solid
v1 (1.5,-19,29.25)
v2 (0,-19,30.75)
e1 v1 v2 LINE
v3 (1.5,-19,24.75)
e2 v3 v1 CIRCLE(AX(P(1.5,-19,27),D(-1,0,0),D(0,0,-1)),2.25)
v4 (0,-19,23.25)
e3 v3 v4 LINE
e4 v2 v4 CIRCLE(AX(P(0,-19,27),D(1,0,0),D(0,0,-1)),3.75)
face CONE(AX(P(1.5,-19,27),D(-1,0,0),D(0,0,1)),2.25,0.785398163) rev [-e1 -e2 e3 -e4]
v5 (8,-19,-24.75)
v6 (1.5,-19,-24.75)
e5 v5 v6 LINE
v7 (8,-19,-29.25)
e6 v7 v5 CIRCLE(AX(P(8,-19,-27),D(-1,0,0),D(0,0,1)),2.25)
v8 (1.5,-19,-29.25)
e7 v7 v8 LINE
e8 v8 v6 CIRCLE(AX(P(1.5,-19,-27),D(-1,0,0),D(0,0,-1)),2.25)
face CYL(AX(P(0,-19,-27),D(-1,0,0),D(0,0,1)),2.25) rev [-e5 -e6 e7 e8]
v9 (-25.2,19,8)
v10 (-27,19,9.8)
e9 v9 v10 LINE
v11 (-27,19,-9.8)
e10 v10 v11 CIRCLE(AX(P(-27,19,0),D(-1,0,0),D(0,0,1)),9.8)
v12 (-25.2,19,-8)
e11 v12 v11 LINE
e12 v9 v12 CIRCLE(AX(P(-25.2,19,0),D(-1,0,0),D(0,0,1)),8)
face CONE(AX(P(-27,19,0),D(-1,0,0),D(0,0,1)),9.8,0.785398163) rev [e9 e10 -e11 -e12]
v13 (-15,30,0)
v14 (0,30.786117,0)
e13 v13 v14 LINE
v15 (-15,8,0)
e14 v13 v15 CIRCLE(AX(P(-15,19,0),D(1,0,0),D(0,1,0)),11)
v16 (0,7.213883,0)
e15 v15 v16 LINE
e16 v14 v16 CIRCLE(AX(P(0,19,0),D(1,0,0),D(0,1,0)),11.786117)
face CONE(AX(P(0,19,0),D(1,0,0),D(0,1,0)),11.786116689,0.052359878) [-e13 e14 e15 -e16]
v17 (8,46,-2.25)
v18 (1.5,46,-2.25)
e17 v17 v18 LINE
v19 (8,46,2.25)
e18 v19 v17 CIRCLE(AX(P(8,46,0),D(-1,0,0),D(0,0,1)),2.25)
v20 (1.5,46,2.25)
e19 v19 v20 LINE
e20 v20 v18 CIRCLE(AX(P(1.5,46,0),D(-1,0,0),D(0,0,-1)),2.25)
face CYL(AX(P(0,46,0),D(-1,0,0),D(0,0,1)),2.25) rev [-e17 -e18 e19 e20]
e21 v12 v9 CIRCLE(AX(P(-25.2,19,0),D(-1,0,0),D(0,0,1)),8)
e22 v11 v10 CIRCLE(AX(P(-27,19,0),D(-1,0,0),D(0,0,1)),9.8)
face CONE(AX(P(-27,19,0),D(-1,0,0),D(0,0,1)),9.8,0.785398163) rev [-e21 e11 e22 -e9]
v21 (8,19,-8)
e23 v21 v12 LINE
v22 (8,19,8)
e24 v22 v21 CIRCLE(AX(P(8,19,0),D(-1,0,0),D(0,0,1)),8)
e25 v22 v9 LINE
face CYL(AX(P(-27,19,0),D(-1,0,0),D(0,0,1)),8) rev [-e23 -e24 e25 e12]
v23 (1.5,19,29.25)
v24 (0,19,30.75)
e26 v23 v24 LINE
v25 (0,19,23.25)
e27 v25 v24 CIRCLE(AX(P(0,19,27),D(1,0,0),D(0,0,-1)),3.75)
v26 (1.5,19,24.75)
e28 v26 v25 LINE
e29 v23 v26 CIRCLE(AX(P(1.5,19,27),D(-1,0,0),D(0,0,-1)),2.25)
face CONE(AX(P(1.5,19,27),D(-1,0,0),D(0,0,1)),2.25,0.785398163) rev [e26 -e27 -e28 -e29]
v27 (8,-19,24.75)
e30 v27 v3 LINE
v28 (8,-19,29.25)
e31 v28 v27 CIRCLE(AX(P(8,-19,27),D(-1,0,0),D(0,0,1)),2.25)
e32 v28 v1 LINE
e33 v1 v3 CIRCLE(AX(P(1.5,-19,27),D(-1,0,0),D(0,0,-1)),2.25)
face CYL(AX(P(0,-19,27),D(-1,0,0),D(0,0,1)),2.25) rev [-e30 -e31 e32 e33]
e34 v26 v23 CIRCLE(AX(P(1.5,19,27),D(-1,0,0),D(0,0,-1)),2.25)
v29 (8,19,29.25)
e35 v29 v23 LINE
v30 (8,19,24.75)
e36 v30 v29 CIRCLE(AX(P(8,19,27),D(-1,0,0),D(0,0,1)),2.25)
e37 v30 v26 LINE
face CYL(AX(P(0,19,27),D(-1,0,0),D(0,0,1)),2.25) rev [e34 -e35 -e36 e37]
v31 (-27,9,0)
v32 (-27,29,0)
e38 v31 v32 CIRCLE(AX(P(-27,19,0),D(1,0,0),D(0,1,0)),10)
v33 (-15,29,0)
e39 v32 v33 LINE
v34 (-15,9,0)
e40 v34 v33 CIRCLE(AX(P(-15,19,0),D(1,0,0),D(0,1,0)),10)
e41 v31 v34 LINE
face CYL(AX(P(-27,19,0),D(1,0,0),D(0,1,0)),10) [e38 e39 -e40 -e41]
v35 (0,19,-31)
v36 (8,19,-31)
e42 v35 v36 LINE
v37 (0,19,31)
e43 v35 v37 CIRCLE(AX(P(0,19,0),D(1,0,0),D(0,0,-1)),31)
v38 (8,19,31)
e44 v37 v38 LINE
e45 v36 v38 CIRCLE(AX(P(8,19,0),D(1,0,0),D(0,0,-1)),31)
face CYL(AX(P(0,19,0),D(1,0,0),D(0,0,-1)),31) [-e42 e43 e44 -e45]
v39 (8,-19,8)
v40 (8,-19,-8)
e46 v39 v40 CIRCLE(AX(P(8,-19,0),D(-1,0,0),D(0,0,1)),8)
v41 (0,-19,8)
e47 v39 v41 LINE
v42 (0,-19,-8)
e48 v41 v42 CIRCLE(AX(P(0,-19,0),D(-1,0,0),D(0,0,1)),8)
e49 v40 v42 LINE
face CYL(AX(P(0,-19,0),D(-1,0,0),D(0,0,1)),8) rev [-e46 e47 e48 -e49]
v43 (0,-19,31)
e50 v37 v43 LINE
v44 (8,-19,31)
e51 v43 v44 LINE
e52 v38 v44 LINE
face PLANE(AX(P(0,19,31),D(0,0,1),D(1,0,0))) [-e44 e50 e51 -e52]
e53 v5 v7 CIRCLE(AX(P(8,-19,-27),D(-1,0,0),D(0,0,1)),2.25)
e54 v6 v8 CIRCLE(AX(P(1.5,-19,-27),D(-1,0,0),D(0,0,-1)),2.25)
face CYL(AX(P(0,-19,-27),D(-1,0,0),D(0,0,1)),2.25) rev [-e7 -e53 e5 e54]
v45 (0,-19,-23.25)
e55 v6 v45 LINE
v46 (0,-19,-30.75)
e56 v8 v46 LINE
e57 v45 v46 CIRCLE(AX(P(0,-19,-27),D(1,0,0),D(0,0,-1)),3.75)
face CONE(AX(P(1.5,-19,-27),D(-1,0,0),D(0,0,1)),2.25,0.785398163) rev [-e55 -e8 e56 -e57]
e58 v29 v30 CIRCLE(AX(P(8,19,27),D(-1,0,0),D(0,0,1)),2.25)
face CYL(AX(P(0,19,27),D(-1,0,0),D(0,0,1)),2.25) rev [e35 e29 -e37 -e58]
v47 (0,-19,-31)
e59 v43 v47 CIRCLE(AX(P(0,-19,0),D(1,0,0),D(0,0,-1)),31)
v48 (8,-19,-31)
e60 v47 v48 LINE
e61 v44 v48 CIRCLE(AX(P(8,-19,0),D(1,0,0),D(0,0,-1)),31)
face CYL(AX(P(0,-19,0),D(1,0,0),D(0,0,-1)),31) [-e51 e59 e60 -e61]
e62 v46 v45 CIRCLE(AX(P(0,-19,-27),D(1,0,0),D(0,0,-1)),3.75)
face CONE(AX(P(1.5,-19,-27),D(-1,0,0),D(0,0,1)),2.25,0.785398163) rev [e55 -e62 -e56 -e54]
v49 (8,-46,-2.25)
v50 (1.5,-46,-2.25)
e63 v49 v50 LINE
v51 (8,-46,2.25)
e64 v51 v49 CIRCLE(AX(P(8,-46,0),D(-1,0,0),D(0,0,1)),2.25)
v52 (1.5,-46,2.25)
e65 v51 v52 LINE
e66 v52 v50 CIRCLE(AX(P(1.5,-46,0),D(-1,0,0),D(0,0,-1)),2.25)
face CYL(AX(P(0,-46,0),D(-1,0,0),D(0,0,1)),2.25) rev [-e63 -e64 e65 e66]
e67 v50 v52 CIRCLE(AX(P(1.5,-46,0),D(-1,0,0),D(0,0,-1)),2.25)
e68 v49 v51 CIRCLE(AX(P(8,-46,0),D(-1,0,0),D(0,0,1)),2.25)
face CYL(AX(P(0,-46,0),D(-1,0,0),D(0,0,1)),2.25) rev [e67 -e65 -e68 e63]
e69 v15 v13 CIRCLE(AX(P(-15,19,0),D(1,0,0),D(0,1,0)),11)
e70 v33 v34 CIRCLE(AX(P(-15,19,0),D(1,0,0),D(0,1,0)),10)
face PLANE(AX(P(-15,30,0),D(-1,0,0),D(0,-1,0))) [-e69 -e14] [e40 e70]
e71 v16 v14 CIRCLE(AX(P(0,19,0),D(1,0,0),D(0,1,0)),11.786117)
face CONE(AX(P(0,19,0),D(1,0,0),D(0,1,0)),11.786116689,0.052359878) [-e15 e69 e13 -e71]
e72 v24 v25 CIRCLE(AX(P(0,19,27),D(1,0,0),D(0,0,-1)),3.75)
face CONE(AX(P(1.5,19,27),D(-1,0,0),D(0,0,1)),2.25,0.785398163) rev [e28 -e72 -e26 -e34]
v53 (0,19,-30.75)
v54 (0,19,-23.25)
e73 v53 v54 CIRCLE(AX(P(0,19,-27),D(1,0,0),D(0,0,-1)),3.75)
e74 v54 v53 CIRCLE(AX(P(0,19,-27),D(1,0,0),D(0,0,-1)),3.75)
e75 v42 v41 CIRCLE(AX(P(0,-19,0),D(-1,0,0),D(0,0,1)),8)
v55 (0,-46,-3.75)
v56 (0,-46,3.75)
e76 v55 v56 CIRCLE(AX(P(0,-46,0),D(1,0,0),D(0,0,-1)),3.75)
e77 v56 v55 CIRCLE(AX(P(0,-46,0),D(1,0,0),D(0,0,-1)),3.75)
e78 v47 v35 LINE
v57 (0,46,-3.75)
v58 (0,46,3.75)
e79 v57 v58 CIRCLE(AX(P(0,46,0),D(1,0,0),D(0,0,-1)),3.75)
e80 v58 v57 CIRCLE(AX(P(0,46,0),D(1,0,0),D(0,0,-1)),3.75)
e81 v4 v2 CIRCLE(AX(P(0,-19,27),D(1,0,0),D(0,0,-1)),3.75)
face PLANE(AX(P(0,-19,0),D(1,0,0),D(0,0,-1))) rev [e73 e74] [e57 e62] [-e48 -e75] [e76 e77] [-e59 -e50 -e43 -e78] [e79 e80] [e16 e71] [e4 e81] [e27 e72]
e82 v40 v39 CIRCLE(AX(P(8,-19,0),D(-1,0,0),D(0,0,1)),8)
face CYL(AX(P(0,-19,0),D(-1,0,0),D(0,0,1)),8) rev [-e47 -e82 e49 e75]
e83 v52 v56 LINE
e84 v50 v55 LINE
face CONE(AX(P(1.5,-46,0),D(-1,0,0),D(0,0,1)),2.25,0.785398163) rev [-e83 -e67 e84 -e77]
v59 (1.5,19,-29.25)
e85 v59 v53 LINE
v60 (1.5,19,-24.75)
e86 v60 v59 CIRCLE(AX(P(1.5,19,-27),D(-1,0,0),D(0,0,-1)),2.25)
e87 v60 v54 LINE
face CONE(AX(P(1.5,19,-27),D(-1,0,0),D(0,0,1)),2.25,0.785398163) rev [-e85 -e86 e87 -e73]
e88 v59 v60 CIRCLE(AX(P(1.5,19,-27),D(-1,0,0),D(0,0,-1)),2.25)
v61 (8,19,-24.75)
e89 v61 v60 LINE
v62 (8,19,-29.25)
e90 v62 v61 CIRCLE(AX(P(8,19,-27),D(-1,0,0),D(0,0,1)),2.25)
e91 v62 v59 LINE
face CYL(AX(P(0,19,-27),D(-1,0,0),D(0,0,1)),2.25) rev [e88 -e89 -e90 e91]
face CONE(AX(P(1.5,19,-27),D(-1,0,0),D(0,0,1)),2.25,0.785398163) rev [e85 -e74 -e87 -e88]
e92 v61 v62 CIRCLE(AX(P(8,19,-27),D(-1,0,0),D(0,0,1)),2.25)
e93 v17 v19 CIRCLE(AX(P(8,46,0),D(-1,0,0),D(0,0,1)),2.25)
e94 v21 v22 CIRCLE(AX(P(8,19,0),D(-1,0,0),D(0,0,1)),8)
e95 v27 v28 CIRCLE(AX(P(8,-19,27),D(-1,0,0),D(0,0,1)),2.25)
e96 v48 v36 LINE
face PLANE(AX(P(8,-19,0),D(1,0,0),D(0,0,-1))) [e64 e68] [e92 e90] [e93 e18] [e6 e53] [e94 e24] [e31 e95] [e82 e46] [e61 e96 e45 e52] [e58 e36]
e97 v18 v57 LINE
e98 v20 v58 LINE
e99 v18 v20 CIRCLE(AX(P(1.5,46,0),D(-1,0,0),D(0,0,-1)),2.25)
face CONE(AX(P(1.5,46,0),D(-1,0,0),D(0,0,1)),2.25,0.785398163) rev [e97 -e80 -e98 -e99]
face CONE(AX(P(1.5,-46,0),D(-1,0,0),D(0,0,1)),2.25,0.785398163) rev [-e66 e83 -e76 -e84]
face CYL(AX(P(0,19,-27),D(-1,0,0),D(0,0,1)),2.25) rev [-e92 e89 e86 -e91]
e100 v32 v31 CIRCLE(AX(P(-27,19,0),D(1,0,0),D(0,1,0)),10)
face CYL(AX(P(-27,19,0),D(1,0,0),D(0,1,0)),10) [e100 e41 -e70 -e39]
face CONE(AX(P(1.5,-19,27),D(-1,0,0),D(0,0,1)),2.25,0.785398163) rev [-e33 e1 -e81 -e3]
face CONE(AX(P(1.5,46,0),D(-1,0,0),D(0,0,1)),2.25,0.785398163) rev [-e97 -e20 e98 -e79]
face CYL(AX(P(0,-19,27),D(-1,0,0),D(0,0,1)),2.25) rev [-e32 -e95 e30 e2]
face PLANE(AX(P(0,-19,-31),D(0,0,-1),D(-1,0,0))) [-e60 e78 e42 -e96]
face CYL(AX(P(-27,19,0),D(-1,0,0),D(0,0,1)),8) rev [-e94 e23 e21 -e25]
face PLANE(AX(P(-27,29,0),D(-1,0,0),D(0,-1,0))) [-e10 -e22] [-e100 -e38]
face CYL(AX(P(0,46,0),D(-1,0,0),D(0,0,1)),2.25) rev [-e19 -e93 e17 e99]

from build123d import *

# Parameters (mm, degrees)
BOSS_EXTRUDE1_DEPTH                  = 8
F_16_0_16_DIAMETER_HOLE1_D           = 16
F_16_0_16_DIAMETER_HOLE2_D           = 16
F_16_0_16_DIAMETER_HOLE2_CSINK_D     = 19.6
F_16_0_16_DIAMETER_HOLE2_CSINK_ANGLE = 90
F_4_5_4_5_DIAMETER_HOLE1_D           = 4.5
CHAMFER1_SIZE                        = 1.5


with BuildPart() as part:
    # Sketch1 → Boss-Extrude1 (new body)
    with BuildSketch(Plane(origin=(8, 0, 0), x_dir=(0, 0, -1), z_dir=(1, 0, 0))):
        with BuildLine():
            Line((31, -19), (31, 19))
            ThreePointArc((31, 19), (0, 50), (-31, 19))
            Line((-31, 19), (-31, -19))
            ThreePointArc((-31, -19), (0, -50), (31, -19))
        make_face()
    extrude(amount=-BOSS_EXTRUDE1_DEPTH)

    # Sketch2 → Revolve1 (revolve)
    with BuildSketch(Plane.XY):
        Polygon((-27, 29), (-27, 19), (0, 19), (0, 30.786116689), (-15, 30), (-15, 29), align=None)
    revolve(axis=Axis((-27, 19, 0), (1, 0, 0)))

    # Ø16.0 (16) Diameter Hole1 (through all)
    with Locations(Plane.ZY):
        with Locations((0, -19)):
            Hole(F_16_0_16_DIAMETER_HOLE1_D / 2)

    # Ø16.0 (16) Diameter Hole2 (through all)
    with Locations(Plane.ZY.offset(27)):
        with Locations((0, 19)):
            CounterSinkHole(F_16_0_16_DIAMETER_HOLE2_D / 2, F_16_0_16_DIAMETER_HOLE2_CSINK_D / 2, counter_sink_angle=F_16_0_16_DIAMETER_HOLE2_CSINK_ANGLE)

    # Ø4.5 (4.5) Diameter Hole1 (through all)
    with Locations(Plane.ZY):
        with Locations((0, 46), (27, 19), (-27, 19), (27, -19), (-27, -19), (0, -46)):
            Hole(F_4_5_4_5_DIAMETER_HOLE1_D / 2)

    # Chamfer1
    chamfer1_edges = [part.edges().sort_by_distance(p)[0] for p in [
        (0, -46, 2.25),
        (0, -19, -24.75),
        (0, -19, 29.25),
        (0, 19, -24.75),
        (0, 19, 29.25),
        (0, 46, 2.25),
    ]]
    chamfer(chamfer1_edges, length=CHAMFER1_SIZE)


solid = part.part
